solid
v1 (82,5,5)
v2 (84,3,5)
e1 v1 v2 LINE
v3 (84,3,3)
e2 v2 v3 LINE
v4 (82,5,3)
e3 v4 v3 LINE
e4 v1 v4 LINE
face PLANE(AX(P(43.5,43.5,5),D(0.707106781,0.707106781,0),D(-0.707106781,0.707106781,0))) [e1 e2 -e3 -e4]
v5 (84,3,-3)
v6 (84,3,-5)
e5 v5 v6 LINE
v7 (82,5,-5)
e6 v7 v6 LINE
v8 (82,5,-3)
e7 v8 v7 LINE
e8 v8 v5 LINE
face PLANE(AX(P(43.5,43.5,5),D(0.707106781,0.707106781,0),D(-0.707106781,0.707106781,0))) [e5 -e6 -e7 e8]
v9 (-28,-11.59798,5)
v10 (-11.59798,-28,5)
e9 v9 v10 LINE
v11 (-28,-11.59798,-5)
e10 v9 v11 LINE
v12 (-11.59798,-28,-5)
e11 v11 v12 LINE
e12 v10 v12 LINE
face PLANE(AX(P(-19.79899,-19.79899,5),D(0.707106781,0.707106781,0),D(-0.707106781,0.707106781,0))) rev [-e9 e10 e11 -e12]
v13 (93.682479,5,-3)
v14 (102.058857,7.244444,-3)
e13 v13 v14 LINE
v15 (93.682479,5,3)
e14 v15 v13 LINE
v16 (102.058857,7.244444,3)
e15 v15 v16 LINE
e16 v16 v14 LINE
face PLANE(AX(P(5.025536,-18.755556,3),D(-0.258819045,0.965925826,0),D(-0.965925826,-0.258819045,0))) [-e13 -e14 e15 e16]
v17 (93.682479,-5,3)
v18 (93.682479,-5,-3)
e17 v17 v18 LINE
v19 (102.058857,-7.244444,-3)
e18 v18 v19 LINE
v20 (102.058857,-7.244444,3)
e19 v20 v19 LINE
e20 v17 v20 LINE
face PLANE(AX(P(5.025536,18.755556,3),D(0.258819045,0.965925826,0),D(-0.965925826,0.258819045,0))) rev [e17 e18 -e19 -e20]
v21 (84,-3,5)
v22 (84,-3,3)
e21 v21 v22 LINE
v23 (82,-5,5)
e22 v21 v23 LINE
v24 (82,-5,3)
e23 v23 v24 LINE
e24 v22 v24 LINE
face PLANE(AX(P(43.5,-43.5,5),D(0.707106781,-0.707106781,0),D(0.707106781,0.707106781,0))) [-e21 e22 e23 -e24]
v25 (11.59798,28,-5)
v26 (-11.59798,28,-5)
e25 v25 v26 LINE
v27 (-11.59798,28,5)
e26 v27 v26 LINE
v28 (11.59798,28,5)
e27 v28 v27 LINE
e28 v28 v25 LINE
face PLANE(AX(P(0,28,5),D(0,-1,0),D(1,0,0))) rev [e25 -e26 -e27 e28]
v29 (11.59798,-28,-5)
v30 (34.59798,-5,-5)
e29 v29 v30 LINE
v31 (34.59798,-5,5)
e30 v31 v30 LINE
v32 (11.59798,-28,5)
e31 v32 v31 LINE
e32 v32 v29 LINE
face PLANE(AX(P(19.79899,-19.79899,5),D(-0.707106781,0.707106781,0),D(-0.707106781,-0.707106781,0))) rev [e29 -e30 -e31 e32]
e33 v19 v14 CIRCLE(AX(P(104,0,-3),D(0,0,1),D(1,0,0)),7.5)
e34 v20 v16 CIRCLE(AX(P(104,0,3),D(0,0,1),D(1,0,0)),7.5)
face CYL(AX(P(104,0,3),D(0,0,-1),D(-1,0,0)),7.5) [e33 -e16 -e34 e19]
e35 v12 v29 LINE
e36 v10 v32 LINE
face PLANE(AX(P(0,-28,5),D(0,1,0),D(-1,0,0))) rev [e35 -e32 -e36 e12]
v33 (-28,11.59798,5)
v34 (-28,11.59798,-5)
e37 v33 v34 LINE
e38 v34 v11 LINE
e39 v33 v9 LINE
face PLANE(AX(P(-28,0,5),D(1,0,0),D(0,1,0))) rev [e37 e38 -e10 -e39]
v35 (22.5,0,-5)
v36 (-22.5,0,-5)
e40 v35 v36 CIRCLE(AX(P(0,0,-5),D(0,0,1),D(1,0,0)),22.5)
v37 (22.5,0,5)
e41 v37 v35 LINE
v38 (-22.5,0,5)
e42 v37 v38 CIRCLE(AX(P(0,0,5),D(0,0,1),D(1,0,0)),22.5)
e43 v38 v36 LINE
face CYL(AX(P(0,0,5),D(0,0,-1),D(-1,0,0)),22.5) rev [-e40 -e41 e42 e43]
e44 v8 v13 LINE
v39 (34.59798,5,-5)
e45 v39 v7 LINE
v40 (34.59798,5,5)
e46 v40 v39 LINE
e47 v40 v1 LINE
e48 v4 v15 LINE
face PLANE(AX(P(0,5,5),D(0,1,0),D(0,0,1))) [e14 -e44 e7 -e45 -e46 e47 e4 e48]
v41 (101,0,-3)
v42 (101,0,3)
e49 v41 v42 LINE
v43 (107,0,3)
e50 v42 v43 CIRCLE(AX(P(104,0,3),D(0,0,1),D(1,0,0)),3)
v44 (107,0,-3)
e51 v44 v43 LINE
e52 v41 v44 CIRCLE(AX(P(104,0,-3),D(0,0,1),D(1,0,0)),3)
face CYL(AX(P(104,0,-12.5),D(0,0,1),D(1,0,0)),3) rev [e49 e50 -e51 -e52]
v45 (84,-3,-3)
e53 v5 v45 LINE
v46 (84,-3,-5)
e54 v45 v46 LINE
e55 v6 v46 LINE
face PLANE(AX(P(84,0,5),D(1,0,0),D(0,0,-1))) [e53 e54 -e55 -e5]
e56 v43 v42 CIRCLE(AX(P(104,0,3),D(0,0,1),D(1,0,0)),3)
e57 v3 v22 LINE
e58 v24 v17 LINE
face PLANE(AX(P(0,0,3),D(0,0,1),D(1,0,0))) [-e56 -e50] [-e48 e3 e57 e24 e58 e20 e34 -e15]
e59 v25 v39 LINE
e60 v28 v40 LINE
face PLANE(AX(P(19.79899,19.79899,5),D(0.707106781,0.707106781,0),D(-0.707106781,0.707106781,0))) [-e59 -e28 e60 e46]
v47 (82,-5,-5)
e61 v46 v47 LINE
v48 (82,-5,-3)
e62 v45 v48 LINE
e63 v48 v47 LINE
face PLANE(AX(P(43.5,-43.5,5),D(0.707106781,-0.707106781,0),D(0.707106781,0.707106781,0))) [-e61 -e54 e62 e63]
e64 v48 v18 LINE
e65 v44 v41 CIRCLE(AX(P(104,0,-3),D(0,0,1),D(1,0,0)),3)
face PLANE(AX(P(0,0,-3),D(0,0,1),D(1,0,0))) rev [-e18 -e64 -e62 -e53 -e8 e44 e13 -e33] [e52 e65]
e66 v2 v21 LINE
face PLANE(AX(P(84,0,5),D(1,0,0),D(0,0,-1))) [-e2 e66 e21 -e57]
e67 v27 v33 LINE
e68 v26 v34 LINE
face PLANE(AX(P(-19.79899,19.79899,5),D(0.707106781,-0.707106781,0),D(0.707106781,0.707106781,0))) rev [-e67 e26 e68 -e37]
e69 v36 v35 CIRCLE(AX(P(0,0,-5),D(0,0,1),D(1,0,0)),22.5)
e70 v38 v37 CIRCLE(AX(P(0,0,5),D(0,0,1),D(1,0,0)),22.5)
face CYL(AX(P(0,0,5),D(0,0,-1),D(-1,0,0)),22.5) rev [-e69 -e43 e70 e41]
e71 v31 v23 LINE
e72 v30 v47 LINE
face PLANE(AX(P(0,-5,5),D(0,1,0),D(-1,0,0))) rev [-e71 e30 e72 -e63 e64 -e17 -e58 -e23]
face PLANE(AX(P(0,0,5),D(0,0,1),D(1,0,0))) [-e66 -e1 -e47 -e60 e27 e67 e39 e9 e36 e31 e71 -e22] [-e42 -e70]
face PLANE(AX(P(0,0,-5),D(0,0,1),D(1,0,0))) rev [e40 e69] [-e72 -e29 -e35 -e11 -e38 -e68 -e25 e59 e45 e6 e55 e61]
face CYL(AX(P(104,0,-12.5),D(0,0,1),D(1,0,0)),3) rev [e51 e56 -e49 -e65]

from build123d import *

# Parameters (mm, degrees)
SKETCH_1_3_R        = 22.5
BOSS_EXTRUDE1_DEPTH = 5
BOSS_EXTRUDE2_DEPTH = 3
SKETCH2_R           = 3
CUT_EXTRUDE1_DEPTH  = 15.5


with BuildPart() as part:
    # Sketch 1_3 → Boss-Extrude1 (new, symmetric)
    with BuildSketch(Plane.XY):
        Polygon((34.597979746, 5), (28, 11.597979746), (11.597979746, 28), (-11.597979746, 28), (-28, 11.597979746), (-28, -11.597979746), (-11.597979746, -28), (11.597979746, -28), (19.798989873, -19.798989873), (28, -11.597979746), (34.597979746, -5), (82, -5), (84, -3), (84, 3), (82, 5), align=None)
        Circle(SKETCH_1_3_R, mode=Mode.SUBTRACT)
    extrude(amount=BOSS_EXTRUDE1_DEPTH, both=True)

    # Sketch 1_3 2 → Boss-Extrude2 (add, symmetric)
    with BuildSketch(Plane.XY):
        with BuildLine():
            Line((93.682479249, 5), (82, 5))
            Line((82, 5), (84, 3))
            Line((84, 3), (84, -3))
            Line((84, -3), (82, -5))
            Line((82, -5), (93.682479249, -5))
            Line((93.682479249, -5), (102.058857162, -7.244443697))
            ThreePointArc((102.058857162, -7.244443697), (111.5, 0), (102.058857162, 7.244443697))
            Line((102.058857162, 7.244443697), (93.682479249, 5))
        make_face()
    extrude(amount=BOSS_EXTRUDE2_DEPTH, both=True)

    # Sketch2 → Cut-Extrude1 (cut, symmetric)
    with BuildSketch(Plane.XY.offset(3)):
        with Locations((104, 0)):
            Circle(SKETCH2_R)
    extrude(amount=CUT_EXTRUDE1_DEPTH, both=True, mode=Mode.SUBTRACT)


solid = part.part
